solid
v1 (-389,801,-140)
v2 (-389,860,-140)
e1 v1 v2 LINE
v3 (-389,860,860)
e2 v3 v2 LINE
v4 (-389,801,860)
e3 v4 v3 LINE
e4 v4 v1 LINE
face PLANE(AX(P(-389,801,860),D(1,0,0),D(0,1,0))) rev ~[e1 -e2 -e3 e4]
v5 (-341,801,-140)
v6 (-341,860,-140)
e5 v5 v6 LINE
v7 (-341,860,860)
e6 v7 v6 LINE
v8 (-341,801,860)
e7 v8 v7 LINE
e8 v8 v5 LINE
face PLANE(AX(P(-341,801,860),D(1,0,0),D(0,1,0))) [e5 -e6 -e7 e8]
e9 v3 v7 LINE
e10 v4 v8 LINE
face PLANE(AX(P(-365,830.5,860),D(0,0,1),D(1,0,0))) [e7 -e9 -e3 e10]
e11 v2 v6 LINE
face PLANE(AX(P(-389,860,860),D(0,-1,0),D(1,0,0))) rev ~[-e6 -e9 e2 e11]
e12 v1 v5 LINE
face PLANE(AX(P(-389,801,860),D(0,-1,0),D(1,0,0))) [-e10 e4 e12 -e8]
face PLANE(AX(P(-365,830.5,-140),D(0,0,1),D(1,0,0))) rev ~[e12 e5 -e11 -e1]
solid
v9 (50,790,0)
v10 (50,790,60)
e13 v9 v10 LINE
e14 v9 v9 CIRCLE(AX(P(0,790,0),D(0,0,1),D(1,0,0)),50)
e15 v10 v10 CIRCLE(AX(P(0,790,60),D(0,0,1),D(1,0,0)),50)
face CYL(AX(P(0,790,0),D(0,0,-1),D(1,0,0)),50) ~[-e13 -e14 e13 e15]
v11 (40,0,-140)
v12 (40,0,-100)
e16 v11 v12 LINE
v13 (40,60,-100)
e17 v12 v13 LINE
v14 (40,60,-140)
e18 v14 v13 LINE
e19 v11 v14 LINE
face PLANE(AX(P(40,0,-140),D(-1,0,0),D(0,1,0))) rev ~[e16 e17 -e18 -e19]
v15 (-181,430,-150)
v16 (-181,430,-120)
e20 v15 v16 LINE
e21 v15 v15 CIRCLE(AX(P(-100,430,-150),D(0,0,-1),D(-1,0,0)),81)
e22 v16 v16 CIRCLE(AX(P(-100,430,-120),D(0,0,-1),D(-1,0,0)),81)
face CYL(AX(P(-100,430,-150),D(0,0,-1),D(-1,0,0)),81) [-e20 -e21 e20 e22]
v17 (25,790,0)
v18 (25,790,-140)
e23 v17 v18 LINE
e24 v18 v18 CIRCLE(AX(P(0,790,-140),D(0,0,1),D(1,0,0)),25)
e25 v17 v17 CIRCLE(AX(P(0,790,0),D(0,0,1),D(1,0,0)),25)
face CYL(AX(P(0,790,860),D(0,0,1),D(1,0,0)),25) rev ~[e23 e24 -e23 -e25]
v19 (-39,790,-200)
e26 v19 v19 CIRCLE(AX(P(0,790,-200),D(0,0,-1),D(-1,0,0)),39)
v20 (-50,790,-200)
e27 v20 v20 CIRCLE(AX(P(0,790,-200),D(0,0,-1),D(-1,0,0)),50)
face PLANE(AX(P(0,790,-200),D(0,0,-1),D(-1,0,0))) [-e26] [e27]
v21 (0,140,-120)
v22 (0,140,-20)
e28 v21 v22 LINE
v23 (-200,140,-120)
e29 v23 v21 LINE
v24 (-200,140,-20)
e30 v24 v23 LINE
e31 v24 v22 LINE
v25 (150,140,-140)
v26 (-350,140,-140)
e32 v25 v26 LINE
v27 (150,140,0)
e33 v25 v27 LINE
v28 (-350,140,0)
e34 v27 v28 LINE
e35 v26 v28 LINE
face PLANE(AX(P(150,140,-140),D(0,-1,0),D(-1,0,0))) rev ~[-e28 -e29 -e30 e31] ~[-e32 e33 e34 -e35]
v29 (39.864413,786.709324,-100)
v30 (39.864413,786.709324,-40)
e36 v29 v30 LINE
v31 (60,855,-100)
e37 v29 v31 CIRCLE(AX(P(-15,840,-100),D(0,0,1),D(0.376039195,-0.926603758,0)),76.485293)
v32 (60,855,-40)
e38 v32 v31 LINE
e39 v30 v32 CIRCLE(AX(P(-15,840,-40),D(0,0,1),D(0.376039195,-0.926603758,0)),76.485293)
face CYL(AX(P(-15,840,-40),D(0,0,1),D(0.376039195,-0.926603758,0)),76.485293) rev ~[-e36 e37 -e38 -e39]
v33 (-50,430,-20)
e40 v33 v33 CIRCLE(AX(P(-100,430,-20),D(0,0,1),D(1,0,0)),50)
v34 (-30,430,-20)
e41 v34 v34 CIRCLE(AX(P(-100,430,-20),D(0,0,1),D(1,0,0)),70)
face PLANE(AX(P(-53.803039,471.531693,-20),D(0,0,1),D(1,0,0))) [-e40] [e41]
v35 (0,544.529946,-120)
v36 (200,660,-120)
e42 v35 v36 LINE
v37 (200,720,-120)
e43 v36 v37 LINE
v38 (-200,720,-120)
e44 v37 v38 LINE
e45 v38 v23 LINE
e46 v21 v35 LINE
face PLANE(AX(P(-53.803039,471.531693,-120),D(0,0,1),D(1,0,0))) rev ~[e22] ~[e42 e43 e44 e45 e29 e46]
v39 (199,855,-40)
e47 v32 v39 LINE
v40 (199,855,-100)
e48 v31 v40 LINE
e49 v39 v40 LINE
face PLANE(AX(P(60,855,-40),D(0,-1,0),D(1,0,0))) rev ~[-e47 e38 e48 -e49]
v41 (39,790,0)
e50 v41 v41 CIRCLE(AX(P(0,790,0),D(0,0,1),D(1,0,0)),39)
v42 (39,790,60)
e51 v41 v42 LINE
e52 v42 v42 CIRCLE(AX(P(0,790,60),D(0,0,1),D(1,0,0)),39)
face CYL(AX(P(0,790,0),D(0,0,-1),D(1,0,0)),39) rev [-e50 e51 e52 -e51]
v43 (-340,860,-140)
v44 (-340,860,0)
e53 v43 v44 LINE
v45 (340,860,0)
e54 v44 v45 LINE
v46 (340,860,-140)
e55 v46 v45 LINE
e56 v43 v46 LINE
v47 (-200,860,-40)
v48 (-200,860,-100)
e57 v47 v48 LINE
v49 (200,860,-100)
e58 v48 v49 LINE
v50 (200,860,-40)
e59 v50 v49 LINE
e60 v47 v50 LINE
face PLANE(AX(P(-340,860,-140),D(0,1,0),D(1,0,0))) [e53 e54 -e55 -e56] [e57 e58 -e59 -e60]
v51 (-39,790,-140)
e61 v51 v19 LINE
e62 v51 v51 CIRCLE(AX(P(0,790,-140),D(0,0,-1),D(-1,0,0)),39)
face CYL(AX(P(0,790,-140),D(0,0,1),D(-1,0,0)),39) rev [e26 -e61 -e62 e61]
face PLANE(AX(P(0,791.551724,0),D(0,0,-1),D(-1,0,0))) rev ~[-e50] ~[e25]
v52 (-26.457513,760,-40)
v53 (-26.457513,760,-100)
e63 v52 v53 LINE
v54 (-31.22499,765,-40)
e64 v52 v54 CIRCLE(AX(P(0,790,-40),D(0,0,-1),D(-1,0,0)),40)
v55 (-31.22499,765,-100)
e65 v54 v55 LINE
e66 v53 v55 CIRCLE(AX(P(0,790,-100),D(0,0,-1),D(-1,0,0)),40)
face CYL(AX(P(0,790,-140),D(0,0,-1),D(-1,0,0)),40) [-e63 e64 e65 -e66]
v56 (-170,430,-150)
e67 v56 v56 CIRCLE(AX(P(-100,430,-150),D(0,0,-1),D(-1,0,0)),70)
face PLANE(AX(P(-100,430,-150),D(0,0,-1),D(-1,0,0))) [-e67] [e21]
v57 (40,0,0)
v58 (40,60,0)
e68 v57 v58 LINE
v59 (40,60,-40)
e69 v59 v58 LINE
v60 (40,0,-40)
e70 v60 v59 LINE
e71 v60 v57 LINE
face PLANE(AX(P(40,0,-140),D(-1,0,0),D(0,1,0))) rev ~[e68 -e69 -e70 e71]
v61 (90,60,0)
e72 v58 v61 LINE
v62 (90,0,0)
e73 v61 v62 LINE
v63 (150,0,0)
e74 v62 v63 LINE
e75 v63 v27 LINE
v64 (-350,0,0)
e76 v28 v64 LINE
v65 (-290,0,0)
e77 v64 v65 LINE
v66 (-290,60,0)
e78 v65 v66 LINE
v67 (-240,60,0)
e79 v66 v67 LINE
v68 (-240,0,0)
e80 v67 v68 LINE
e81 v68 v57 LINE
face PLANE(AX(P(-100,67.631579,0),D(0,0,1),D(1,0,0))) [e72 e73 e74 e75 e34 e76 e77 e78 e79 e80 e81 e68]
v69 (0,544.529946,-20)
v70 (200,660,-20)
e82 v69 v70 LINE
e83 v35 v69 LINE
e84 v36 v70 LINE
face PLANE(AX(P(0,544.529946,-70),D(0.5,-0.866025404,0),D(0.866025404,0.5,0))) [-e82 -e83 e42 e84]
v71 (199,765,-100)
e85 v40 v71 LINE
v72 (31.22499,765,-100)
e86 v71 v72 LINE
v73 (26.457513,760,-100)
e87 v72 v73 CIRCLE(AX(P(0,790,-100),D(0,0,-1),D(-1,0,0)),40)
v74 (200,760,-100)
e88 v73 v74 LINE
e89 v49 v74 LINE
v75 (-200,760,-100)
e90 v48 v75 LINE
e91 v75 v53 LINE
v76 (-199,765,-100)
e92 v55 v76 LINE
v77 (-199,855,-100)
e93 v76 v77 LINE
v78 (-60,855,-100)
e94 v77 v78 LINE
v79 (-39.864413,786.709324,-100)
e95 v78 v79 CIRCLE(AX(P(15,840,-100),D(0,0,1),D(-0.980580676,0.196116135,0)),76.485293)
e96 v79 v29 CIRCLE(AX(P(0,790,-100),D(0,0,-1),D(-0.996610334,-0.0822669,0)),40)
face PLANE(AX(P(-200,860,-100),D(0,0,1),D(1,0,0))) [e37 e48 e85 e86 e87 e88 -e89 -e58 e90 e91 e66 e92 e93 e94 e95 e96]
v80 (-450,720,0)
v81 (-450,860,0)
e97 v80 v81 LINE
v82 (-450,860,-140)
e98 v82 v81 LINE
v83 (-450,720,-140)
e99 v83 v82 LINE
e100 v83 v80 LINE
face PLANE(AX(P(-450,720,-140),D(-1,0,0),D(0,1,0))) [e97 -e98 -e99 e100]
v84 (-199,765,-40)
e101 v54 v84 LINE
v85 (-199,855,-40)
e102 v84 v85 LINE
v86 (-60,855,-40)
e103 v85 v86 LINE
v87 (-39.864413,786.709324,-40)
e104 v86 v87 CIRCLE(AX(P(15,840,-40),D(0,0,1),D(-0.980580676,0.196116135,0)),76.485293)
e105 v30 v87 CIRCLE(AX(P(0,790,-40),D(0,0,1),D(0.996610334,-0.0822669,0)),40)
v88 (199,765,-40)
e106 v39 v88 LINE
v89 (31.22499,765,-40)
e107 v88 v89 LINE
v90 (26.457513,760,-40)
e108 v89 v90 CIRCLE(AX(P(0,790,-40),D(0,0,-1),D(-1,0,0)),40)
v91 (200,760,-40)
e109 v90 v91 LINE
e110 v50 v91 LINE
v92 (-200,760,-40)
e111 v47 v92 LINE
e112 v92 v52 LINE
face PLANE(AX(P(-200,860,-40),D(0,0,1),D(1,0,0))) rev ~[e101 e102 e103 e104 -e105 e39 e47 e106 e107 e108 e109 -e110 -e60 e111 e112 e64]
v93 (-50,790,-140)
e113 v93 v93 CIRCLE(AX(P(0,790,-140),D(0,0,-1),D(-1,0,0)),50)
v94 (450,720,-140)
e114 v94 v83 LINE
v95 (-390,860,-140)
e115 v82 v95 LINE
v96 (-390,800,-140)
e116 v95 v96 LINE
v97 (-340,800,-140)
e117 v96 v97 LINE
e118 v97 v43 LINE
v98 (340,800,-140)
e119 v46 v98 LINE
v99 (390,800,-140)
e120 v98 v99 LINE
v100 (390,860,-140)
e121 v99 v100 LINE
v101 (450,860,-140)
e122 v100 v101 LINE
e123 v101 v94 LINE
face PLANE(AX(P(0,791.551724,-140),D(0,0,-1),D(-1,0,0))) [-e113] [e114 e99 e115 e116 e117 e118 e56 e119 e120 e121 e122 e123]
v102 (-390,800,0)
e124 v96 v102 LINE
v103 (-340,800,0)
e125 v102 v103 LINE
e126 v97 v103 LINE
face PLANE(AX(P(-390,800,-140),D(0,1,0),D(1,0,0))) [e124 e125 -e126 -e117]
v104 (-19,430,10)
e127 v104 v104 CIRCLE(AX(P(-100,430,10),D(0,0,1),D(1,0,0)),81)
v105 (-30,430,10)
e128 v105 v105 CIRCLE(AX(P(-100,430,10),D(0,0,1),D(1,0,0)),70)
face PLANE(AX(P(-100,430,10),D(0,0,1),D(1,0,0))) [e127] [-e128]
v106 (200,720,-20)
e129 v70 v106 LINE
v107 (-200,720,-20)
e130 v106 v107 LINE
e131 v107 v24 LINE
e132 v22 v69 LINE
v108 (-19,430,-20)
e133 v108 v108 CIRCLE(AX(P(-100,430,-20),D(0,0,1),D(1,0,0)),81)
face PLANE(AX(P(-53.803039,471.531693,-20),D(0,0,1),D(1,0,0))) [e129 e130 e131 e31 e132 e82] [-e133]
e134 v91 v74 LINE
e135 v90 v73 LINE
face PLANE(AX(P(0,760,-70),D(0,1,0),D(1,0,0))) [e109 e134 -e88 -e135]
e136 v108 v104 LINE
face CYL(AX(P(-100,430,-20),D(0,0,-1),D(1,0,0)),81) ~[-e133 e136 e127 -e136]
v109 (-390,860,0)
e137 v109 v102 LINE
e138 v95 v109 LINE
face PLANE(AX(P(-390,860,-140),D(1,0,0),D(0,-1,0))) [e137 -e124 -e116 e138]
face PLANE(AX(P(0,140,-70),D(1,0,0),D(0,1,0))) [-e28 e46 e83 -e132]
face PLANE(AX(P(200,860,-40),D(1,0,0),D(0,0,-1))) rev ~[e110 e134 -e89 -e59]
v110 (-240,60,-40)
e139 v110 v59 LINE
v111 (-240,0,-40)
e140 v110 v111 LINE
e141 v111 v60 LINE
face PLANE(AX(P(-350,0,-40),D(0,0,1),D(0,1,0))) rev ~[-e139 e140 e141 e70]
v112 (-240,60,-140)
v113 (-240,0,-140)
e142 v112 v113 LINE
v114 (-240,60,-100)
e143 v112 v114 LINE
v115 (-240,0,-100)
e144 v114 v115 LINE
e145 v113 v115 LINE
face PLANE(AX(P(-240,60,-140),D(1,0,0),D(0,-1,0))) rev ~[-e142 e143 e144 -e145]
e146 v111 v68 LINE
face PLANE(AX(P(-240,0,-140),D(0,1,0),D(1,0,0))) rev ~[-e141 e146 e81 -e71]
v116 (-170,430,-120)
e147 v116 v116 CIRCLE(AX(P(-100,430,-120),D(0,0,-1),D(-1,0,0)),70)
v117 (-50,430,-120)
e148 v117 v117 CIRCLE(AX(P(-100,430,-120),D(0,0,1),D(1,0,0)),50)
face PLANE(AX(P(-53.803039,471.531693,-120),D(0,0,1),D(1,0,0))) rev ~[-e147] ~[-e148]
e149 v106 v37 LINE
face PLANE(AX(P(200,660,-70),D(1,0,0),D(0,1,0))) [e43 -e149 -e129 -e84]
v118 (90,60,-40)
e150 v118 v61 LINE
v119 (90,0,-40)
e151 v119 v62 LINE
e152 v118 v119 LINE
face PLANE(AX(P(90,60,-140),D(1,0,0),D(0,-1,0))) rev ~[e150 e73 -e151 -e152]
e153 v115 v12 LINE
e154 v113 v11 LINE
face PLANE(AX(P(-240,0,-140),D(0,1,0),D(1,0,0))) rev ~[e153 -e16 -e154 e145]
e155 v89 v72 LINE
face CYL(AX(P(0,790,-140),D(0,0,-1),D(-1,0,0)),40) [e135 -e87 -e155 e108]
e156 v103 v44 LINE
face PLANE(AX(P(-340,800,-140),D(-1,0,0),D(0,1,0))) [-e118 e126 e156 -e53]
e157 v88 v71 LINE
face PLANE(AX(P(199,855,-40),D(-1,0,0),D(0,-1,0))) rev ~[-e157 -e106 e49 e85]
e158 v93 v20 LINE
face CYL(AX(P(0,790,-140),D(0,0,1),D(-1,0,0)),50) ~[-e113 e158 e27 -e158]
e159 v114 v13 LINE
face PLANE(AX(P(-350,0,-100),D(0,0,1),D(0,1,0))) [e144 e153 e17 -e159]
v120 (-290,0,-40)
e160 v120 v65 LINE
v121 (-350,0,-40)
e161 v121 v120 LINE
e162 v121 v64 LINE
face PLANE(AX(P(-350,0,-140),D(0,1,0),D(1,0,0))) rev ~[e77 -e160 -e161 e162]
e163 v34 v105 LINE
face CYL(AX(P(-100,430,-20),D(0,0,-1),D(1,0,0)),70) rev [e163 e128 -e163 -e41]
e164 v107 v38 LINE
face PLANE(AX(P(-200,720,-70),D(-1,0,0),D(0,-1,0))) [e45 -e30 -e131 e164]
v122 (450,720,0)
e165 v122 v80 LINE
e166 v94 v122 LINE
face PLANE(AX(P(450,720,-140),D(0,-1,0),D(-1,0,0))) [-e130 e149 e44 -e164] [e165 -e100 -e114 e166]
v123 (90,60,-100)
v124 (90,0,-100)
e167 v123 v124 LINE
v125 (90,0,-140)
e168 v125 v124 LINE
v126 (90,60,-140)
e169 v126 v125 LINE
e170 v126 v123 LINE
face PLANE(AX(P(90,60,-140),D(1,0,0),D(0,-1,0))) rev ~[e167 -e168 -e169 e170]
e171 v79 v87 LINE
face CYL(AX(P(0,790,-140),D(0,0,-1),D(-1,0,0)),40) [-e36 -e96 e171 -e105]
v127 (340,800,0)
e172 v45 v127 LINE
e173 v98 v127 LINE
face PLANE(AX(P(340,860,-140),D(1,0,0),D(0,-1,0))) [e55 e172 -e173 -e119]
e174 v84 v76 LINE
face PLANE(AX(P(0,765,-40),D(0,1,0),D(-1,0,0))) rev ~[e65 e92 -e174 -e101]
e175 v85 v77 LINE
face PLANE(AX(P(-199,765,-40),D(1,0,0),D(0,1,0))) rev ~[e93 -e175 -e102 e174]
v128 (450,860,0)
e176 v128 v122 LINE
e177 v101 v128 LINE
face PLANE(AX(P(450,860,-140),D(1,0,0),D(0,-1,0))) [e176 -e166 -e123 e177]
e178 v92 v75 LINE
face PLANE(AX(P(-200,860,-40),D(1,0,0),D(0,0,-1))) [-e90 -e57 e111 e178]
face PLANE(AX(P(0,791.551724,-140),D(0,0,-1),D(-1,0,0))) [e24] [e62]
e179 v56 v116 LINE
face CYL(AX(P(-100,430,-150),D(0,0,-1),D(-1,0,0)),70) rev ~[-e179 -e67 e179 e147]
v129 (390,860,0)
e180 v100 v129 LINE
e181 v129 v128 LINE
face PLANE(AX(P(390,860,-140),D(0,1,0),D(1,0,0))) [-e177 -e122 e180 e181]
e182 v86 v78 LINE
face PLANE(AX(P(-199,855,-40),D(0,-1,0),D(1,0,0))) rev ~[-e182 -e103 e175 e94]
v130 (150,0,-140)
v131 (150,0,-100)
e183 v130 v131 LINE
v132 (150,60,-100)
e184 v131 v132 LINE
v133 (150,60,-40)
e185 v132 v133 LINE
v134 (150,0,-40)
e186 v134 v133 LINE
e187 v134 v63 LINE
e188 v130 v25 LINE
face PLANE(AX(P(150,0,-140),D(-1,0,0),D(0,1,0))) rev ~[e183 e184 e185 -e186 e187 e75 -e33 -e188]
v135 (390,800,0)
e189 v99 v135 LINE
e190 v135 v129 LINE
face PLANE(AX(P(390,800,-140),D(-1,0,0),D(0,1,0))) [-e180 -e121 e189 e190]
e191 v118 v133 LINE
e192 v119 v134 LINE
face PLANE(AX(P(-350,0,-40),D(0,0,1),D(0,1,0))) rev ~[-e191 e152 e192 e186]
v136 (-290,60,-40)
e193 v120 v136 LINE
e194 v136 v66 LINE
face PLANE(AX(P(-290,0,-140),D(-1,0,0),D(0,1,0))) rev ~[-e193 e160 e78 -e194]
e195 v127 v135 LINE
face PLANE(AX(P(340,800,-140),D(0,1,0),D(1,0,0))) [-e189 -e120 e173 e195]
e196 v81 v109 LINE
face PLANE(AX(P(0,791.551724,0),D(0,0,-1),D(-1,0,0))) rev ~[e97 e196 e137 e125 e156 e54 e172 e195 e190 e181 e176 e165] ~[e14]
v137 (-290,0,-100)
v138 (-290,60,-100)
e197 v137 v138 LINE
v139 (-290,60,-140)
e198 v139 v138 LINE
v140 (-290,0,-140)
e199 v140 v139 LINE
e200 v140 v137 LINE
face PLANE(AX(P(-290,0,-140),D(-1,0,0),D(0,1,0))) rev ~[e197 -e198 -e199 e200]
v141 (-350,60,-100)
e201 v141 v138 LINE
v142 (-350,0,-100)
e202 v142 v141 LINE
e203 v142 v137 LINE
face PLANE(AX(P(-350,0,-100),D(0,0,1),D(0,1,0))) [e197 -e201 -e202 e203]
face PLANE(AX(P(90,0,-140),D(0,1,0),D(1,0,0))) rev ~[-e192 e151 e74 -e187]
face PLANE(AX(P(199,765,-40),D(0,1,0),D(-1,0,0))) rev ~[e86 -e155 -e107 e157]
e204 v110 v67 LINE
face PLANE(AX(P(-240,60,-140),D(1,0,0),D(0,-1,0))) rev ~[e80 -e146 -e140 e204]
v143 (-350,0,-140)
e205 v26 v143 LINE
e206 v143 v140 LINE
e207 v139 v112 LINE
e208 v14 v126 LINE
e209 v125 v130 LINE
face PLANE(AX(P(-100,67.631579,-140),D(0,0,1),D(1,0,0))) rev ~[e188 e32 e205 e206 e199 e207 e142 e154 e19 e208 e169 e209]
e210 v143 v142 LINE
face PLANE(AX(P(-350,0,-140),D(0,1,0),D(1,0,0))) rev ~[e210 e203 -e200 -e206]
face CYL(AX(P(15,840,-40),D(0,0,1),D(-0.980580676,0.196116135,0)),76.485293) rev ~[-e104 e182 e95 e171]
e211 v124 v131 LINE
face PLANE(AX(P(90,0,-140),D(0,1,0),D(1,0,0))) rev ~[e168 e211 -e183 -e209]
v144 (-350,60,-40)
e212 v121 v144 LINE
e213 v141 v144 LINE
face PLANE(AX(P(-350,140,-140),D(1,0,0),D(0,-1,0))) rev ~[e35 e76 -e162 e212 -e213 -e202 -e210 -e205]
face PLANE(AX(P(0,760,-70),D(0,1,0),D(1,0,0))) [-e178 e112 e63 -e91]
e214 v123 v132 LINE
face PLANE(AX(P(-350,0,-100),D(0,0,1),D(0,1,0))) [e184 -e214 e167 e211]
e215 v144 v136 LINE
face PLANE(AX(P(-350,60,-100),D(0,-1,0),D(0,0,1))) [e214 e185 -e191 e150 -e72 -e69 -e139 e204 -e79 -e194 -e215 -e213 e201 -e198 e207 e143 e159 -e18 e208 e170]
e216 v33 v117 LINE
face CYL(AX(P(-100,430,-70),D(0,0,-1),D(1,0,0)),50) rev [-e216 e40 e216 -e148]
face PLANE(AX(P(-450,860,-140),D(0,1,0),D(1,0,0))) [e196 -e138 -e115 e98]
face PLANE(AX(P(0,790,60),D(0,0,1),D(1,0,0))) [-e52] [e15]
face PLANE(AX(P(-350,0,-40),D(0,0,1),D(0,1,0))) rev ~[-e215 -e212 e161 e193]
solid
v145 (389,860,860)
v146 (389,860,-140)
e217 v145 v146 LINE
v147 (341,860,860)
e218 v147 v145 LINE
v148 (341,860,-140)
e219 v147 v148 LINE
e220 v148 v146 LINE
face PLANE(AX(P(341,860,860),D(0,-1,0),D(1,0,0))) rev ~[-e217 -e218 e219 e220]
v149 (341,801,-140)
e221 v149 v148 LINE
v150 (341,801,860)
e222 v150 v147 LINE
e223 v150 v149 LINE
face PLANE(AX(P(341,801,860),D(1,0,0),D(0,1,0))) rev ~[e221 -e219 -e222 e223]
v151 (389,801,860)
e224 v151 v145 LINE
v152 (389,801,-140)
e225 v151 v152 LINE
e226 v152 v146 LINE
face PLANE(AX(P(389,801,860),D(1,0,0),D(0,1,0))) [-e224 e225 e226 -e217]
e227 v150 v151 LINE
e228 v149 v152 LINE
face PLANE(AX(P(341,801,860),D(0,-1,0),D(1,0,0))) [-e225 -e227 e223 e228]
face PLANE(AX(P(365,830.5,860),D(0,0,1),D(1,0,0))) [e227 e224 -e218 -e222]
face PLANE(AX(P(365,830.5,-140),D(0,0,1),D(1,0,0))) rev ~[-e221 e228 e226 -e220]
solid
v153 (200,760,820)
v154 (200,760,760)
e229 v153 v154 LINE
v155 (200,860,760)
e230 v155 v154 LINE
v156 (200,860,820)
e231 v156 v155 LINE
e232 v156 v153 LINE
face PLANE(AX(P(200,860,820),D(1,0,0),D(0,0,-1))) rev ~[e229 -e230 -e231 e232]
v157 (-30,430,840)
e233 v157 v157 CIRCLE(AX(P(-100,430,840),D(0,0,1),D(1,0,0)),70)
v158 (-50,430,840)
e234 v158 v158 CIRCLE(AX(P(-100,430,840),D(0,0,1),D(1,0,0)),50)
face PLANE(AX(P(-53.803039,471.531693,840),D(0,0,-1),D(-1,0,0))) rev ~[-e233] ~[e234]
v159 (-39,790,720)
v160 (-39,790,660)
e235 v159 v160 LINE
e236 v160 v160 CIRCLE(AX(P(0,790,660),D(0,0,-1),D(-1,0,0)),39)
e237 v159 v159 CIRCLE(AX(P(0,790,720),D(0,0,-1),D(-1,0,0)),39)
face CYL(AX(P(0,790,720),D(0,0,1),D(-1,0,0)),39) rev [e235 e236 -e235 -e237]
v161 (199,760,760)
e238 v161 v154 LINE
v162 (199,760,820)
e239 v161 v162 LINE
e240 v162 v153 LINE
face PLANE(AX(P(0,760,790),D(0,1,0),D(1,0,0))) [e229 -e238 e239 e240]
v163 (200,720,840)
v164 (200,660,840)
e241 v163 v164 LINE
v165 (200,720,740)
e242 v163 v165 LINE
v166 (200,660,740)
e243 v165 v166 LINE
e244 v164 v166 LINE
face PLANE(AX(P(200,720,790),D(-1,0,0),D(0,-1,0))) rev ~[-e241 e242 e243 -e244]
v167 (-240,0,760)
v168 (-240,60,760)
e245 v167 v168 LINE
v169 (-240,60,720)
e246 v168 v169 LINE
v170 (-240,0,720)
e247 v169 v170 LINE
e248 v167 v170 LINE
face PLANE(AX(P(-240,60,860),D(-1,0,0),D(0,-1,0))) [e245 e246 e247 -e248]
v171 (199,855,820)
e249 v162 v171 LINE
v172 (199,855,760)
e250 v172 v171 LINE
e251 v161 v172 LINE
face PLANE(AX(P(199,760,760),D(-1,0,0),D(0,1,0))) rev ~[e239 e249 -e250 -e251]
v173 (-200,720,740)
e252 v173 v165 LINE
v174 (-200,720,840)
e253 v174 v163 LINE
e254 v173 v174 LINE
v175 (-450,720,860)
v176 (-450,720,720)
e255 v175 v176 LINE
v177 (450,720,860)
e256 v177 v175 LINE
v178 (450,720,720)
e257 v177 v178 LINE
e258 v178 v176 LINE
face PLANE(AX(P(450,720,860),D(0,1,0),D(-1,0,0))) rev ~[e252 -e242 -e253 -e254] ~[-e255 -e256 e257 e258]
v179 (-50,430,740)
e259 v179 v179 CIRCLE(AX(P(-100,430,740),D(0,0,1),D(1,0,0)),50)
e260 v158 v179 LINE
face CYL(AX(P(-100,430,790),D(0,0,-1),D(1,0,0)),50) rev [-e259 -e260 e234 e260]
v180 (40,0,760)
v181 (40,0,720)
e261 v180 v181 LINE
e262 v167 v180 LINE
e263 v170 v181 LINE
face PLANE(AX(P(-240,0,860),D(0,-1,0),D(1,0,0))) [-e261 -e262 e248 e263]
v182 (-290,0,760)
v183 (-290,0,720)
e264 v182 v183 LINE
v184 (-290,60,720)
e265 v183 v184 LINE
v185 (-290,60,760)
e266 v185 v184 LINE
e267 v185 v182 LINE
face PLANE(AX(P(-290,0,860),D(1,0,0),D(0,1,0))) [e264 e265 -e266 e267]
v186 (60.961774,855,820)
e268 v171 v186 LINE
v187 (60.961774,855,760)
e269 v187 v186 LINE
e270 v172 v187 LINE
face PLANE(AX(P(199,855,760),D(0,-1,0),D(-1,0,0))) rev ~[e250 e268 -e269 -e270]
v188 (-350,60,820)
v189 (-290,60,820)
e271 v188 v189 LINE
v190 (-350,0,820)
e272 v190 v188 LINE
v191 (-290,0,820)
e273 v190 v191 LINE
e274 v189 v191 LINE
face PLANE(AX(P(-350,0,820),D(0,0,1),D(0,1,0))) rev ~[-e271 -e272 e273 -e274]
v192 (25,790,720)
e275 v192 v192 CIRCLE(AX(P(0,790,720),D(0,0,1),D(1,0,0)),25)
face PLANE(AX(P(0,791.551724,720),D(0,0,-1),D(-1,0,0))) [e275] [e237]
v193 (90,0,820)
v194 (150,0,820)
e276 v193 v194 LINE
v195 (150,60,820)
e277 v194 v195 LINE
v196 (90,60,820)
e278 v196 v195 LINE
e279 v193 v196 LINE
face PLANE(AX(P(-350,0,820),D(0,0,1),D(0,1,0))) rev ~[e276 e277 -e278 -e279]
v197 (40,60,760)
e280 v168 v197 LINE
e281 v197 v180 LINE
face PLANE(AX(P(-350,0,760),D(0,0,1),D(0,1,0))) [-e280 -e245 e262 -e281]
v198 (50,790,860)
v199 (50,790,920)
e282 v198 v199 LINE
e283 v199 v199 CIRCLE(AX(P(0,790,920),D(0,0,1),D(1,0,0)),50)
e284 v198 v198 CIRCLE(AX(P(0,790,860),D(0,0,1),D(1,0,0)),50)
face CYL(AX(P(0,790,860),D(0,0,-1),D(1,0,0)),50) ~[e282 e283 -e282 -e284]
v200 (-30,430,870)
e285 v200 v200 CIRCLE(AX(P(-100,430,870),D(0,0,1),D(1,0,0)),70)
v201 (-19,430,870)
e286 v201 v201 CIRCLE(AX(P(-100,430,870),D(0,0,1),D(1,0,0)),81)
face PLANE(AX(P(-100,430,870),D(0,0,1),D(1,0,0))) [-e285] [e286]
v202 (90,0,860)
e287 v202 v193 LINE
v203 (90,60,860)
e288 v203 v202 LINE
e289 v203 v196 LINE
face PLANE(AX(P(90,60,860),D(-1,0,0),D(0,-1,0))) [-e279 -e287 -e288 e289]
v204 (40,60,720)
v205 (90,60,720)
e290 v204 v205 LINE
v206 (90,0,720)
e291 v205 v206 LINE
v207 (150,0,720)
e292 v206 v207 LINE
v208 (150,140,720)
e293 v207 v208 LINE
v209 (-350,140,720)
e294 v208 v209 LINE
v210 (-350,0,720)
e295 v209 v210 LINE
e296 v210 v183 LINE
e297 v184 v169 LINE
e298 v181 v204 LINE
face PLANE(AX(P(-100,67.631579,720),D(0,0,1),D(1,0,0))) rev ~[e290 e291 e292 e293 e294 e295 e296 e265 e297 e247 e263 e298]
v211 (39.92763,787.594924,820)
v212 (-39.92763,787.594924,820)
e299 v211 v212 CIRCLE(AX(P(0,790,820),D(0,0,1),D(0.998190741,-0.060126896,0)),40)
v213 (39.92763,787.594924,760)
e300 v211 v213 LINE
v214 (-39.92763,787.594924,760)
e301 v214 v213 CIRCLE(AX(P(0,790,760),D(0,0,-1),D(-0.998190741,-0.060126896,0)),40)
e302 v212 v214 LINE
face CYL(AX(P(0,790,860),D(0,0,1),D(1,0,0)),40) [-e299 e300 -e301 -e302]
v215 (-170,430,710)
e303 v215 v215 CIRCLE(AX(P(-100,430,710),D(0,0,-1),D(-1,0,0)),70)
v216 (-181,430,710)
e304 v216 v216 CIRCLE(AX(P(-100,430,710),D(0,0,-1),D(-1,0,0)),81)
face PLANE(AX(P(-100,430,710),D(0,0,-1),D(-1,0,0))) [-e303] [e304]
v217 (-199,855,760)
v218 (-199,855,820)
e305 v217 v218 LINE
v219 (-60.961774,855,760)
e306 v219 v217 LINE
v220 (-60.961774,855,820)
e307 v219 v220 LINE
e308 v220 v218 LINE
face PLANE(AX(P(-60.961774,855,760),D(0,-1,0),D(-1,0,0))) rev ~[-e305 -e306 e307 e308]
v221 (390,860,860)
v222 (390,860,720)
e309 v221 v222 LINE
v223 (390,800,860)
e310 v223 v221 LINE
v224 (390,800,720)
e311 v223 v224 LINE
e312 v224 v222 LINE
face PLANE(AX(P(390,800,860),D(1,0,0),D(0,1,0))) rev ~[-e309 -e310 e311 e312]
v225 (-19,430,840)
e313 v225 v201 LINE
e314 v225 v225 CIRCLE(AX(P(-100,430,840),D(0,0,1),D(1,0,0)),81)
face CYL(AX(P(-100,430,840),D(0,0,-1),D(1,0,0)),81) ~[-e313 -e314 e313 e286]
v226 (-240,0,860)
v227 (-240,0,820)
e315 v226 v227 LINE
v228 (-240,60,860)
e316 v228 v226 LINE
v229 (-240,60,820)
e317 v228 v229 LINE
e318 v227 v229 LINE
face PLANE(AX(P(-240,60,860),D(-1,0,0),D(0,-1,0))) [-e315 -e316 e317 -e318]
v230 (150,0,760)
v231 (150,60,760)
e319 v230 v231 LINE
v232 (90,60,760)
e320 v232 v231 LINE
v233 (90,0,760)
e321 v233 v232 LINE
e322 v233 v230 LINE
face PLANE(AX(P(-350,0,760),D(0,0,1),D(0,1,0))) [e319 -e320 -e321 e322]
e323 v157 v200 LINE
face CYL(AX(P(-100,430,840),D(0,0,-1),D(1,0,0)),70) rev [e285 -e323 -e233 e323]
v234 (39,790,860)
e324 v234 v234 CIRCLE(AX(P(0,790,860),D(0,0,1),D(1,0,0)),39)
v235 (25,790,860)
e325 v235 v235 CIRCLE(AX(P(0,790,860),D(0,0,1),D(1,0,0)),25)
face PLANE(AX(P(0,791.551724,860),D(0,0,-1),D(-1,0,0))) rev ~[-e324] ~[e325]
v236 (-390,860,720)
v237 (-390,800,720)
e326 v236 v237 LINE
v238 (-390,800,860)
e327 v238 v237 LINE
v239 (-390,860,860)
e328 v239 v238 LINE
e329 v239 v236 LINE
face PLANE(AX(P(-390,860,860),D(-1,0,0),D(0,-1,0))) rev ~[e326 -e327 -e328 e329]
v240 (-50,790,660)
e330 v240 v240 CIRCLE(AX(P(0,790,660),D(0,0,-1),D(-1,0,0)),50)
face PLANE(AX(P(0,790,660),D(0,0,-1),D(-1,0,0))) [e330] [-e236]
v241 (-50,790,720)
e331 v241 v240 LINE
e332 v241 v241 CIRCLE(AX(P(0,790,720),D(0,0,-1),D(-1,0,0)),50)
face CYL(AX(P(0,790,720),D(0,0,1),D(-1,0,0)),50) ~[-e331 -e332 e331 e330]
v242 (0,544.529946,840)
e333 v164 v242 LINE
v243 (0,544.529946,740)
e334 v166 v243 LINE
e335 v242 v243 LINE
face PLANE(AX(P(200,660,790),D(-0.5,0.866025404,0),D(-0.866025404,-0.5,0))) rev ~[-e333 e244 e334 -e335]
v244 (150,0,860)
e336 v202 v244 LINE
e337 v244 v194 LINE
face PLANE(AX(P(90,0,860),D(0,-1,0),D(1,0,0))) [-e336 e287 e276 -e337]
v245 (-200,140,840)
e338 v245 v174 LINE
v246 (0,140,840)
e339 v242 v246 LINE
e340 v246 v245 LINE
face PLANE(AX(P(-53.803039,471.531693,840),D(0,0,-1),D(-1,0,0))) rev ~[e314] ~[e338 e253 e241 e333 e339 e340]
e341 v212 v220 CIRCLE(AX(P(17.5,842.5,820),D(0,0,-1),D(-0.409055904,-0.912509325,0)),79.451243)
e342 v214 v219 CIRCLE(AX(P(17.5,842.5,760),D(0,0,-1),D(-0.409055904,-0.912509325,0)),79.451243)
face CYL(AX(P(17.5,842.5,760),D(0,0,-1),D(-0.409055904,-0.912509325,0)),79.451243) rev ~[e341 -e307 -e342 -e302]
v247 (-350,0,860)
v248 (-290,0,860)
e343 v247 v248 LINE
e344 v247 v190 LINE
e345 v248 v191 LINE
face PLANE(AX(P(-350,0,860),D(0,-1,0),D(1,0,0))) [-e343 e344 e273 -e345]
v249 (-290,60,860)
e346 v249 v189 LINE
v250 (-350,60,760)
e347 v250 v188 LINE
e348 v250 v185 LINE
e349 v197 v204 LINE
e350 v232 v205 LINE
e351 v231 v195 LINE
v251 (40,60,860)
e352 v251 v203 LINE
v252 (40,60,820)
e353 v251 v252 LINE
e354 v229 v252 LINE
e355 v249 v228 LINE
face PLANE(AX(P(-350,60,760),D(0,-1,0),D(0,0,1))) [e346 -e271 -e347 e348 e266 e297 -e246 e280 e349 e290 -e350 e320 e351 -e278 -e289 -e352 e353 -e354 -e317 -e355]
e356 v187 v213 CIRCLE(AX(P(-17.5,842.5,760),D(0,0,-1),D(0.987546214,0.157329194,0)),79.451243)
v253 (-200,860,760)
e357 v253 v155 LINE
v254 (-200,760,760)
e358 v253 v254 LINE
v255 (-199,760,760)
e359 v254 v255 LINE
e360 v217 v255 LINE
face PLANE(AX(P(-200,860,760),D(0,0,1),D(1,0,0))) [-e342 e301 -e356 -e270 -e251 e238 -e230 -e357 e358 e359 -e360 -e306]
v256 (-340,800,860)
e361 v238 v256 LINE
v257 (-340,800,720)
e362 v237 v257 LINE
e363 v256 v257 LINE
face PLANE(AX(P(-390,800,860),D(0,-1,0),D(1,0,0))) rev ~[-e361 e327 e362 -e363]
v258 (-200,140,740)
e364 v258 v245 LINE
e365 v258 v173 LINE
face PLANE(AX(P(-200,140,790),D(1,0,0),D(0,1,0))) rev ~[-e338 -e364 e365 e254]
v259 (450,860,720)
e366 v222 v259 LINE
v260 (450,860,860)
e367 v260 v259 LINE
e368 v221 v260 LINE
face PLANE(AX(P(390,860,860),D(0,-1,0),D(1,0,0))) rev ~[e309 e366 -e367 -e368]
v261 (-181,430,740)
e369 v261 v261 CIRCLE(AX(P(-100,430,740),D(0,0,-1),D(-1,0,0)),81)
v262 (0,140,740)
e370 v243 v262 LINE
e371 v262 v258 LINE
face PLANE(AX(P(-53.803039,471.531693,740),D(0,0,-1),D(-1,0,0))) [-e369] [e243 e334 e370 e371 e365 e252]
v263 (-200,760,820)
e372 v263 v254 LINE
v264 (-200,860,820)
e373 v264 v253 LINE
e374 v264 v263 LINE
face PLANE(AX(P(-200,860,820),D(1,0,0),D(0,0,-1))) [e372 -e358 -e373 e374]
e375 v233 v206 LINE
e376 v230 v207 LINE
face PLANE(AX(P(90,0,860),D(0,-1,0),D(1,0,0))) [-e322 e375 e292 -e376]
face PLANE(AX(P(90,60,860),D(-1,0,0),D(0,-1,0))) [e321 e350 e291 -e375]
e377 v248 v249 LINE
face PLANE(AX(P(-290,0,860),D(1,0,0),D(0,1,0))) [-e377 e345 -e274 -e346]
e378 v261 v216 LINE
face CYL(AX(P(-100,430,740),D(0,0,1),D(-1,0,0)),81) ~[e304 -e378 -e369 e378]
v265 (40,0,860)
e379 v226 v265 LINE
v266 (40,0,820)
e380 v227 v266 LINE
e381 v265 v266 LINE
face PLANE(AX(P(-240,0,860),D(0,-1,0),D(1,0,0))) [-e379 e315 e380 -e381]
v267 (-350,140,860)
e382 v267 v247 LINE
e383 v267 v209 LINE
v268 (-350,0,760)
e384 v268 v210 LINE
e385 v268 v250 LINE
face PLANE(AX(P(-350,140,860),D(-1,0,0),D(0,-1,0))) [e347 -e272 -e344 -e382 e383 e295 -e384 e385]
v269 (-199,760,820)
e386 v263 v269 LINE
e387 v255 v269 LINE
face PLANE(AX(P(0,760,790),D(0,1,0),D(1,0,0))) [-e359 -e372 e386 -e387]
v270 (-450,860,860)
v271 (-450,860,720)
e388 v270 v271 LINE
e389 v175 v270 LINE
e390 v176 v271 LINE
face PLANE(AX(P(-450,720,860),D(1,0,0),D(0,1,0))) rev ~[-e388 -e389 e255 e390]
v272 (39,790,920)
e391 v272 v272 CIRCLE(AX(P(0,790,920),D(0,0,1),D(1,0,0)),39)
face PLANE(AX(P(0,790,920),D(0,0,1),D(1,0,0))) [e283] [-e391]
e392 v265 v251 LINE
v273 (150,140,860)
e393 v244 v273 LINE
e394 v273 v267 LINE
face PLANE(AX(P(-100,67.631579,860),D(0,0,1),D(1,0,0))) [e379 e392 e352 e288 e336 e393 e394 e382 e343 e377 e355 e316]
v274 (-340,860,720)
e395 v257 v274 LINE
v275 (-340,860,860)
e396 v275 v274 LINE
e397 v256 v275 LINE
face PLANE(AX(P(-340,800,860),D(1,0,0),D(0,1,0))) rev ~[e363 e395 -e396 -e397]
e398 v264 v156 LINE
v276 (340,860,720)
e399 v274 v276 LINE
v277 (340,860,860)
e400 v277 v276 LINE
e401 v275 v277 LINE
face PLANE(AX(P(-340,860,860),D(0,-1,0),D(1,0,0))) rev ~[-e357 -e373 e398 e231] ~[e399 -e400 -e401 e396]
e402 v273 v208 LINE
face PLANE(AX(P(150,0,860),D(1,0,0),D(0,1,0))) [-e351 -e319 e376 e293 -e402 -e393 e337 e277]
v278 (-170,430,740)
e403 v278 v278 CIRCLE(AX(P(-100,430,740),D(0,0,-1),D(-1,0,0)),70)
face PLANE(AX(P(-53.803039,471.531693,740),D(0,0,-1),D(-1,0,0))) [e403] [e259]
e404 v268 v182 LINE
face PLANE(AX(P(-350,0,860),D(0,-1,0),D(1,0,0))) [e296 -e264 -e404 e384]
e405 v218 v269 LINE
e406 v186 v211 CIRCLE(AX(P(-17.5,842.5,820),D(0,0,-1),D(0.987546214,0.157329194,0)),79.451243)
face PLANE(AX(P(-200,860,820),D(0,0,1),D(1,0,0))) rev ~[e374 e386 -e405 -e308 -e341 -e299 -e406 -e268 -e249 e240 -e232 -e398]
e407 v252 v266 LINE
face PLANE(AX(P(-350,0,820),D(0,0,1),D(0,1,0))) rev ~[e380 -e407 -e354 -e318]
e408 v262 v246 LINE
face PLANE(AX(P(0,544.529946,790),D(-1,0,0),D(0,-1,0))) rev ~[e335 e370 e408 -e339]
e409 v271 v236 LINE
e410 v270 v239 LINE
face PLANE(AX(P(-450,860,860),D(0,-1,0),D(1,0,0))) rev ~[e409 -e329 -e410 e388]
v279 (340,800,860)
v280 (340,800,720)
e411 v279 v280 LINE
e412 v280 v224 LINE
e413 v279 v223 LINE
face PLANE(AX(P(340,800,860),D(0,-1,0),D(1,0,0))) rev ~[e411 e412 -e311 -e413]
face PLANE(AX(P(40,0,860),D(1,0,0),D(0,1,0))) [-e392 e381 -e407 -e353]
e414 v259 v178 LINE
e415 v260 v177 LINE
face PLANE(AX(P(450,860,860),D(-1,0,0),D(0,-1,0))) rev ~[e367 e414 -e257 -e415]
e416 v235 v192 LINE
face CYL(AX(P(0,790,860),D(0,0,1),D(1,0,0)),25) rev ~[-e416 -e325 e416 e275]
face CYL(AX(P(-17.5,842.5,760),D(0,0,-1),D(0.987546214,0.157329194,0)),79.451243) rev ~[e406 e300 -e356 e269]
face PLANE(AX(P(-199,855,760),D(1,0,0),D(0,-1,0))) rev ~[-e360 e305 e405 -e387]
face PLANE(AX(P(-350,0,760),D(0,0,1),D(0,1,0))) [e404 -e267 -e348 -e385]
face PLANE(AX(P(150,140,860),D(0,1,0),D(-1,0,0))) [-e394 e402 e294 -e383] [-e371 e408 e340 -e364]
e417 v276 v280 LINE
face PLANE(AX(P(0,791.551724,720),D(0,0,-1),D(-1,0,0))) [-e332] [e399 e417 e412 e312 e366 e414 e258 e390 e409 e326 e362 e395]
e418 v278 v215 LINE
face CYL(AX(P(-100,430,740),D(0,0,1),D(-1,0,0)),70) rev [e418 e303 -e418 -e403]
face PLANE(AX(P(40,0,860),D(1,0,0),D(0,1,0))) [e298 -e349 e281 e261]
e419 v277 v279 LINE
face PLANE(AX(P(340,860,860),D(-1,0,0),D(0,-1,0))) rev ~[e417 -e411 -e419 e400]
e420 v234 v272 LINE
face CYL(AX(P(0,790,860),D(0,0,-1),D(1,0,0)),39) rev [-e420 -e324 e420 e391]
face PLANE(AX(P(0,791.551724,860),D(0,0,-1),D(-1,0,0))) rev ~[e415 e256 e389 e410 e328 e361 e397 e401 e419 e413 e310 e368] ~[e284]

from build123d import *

# Parameters (mm, degrees)
FOOT_BASE_DEPTH               = 140
FOOT_BLOCK_SKETCH_W           = 500
FOOT_BLOCK_SKETCH_H           = 140
FOOT_BLOCK_DEPTH              = 140
FOOT_SLOT_SKETCH_W            = 50
FOOT_SLOT_SKETCH_H            = 60
FOOT_SLOT_CUT_DEPTH           = 140
FOOT_NOTCH_SKETCH_W           = 60
FOOT_NOTCH_SKETCH_H           = 60
FOOT_NOTCH_CUT_DEPTH          = 500
UPRIGHT_COLUMN_DEPTH          = 500
COLUMN_RELIEF_SKETCH_W        = 50
COLUMN_RELIEF_SKETCH_H        = 60
COLUMN_RELIEF_CUT_DEPTH       = 500
TOP_BEAM_DEPTH                = 140
TOP_BEAM_EXTENSION_DEPTH      = 140
CROSS_RAILS_SKETCH_W          = 48
CROSS_RAILS_SKETCH_H          = 59
CROSS_RAILS_DEPTH             = 1000
CROSS_RAILS_2_DEPTH           = 1000
AXLE_BORE_50_SKETCH_R         = 25
AXLE_BORE_50_DEPTH            = 1000
BEAM_POCKET_SKETCH_W          = 400
BEAM_POCKET_SKETCH_H          = 60
BEAM_POCKET_CUT_DEPTH         = 100
POCKET_INSERT_A_DEPTH         = 60
POCKET_INSERT_B_DEPTH         = 60
POCKET_INSERT_B_2_DEPTH       = 60
ROLLER_80_A_SKETCH_R          = 40
ROLLER_80_A_DEPTH             = 140
ROLLER_80_B_SKETCH_R          = 40
ROLLER_80_B_DEPTH             = 140
BUSHING_RING_100_A_SKETCH_R   = 50
BUSHING_RING_100_A_SKETCH_R_2 = 39
BUSHING_RING_100_A_DEPTH      = 60
BUSHING_BORE_50_SKETCH_R      = 25
BUSHING_BORE_50_DEPTH         = 1000
BUSHING_RING_100_B_SKETCH_R   = 50
BUSHING_RING_100_B_SKETCH_R_2 = 39
BUSHING_RING_100_B_DEPTH      = 60
BUSHING_RING_100_C_SKETCH_R   = 50
BUSHING_RING_100_C_SKETCH_R_2 = 39
BUSHING_RING_100_C_DEPTH      = 60
BUSHING_RING_100_D_SKETCH_R   = 50
BUSHING_RING_100_D_SKETCH_R_2 = 39
BUSHING_RING_100_D_DEPTH      = 60
SECOND_TRESTLE_BEAM_SKETCH_R  = 50
SECOND_TRESTLE_BEAM_DEPTH     = 50
SECOND_COLUMN_SKETCH_R        = 50
SECOND_COLUMN_DEPTH           = 50
RAIL_CLEARANCE_SKETCH_W       = 500
RAIL_CLEARANCE_SKETCH_H       = 140
RAIL_CLEARANCE_CUT_DEPTH      = 1000
SECOND_FOOT_BASE_DEPTH        = 140
SECOND_FOOT_BLOCK_DEPTH       = 140
SECOND_FOOT_NOTCH_SKETCH_W    = 60
SECOND_FOOT_NOTCH_SKETCH_H    = 60
SECOND_FOOT_NOTCH_CUT_DEPTH   = 500
COLUMN_RING_140_A_SKETCH_R    = 81
COLUMN_RING_140_A_SKETCH_R_2  = 70
COLUMN_RING_140_A_DEPTH       = 30
COLUMN_RING_140_B_SKETCH_R    = 81
COLUMN_RING_140_B_SKETCH_R_2  = 70
COLUMN_RING_140_B_DEPTH       = 30
COLUMN_RING_140_C_SKETCH_R    = 81
COLUMN_RING_140_C_SKETCH_R_2  = 70
COLUMN_RING_140_C_DEPTH       = 30
COLUMN_START                  = 30
COLUMN_RING_140_D_SKETCH_R    = 81
COLUMN_RING_140_D_SKETCH_R_2  = 70
COLUMN_RING_140_D_DEPTH       = 30


with BuildPart() as part:
    # Foot Base Sketch → Foot Base (new body)
    with BuildSketch(Plane(origin=(0, 0, 0), x_dir=(1, 0, 0), z_dir=(0, 1, 0))):
        Polygon((-250, 0), (-250, 140), (-190, 140), (-190, 80), (-140, 80), (-140, 140), (140, 140), (140, 80), (190, 80), (190, 140), (250, 140), (250, 0), align=None)
    extrude(amount=FOOT_BASE_DEPTH)

    # Foot Block Sketch → Foot Block (add)
    with BuildSketch(Plane.XY):
        with Locations((0, 70)):
            Rectangle(FOOT_BLOCK_SKETCH_W, FOOT_BLOCK_SKETCH_H)
    extrude(amount=-FOOT_BLOCK_DEPTH)

    # Foot Slot Sketch → Foot Slot Cut (cut)
    with BuildSketch(Plane.XY):
        with Locations((-165, 30)):
            Rectangle(FOOT_SLOT_SKETCH_W, FOOT_SLOT_SKETCH_H)
        with Locations((165, 30)):
            Rectangle(FOOT_SLOT_SKETCH_W, FOOT_SLOT_SKETCH_H)
    extrude(amount=-FOOT_SLOT_CUT_DEPTH, mode=Mode.SUBTRACT)

    # Foot Notch Sketch → Foot Notch Cut (cut)
    with BuildSketch(Plane.ZY.offset(250)):
        with Locations((-70, 30)):
            Rectangle(FOOT_NOTCH_SKETCH_W, FOOT_NOTCH_SKETCH_H)
    extrude(amount=-FOOT_NOTCH_CUT_DEPTH, mode=Mode.SUBTRACT)



with BuildPart() as body_2:
    # Upright Column Sketch → Upright Column (new body)
    with BuildSketch(Plane.ZY.offset(250)):
        Polygon((760, 60), (820, 60), (820, 0), (860, 0), (860, 140), (720, 140), (720, 0), (760, 0), align=None)
    extrude(amount=-UPRIGHT_COLUMN_DEPTH)

    # Column Relief Sketch → Column Relief Cut (cut)
    with BuildSketch(Plane(origin=(0, 0, 720), x_dir=(-1, 0, 0), z_dir=(0, 0, -1))):
        with Locations((-165, 30)):
            Rectangle(COLUMN_RELIEF_SKETCH_W, COLUMN_RELIEF_SKETCH_H)
        with Locations((165, 30)):
            Rectangle(COLUMN_RELIEF_SKETCH_W, COLUMN_RELIEF_SKETCH_H)
    extrude(amount=-COLUMN_RELIEF_CUT_DEPTH, mode=Mode.SUBTRACT)



with BuildPart() as body_3:
    # Top Beam Sketch → Top Beam (new body)
    with BuildSketch(Plane.XY.offset(860)):
        Polygon((450, 720), (-450, 720), (-450, 860), (-390, 860), (-390, 800), (-340, 800), (-340, 860), (340, 860), (340, 800), (390, 800), (390, 860), (450, 860), align=None)
    extrude(amount=-TOP_BEAM_DEPTH)


with BuildPart() as body_4:
    # Top Beam Extension Sketch → Top Beam Extension (new body)
    with BuildSketch(Plane(origin=(0, 0, -140), x_dir=(-1, 0, 0), z_dir=(0, 0, -1))):
        Polygon((-450, 860), (-450, 720), (450, 720), (450, 860), (390, 860), (390, 800), (340, 800), (340, 860), (-340, 860), (-340, 800), (-390, 800), (-390, 860), align=None)
    extrude(amount=-TOP_BEAM_EXTENSION_DEPTH)


with BuildPart() as body_5:
    # Cross Rails Sketch → Cross Rails (new body)
    with BuildSketch(Plane.XY.offset(860)):
        with Locations((-365, 830.5)):
            Rectangle(CROSS_RAILS_SKETCH_W, CROSS_RAILS_SKETCH_H)
    extrude(amount=-CROSS_RAILS_DEPTH)


with BuildPart() as body_6:
    # Cross Rails Sketch → Cross Rails 2 (new body)
    with BuildSketch(Plane.XY.offset(860)):
        with Locations((365, 830.5)):
            Rectangle(CROSS_RAILS_SKETCH_W, CROSS_RAILS_SKETCH_H)
    extrude(amount=-CROSS_RAILS_2_DEPTH)


with BuildPart() as axle_bore_50_tool:
    # Axle Bore Ø50 Sketch → Axle Bore Ø50 (new body)
    with BuildSketch(Plane.XY.offset(860)):
        with Locations((0, 790)):
            Circle(AXLE_BORE_50_SKETCH_R)
    extrude(amount=-AXLE_BORE_50_DEPTH)


with BuildPart() as body_3_1:
    add(body_3.part)

    # Axle Bore Ø50: cut by axle_bore_50_tool
    add(axle_bore_50_tool.part, mode=Mode.SUBTRACT)


with BuildPart() as body_4_1:
    add(body_4.part)

    # Axle Bore Ø50: cut by axle_bore_50_tool
    add(axle_bore_50_tool.part, mode=Mode.SUBTRACT)


with BuildPart() as beam_pocket_cut_tool:
    # Beam Pocket Sketch → Beam Pocket Cut (new body)
    with BuildSketch(Plane(origin=(0, 860, 0), x_dir=(1, 0, 0), z_dir=(0, 1, 0))):
        with Locations((0, -790)):
            Rectangle(BEAM_POCKET_SKETCH_W, BEAM_POCKET_SKETCH_H)
        with Locations((0, 70)):
            Rectangle(BEAM_POCKET_SKETCH_W, BEAM_POCKET_SKETCH_H)
    extrude(amount=-BEAM_POCKET_CUT_DEPTH)


with BuildPart() as body_3_2:
    add(body_3_1.part)

    # Beam Pocket Cut: cut by beam_pocket_cut_tool
    add(beam_pocket_cut_tool.part, mode=Mode.SUBTRACT)

    # Pocket Insert A Sketch → Pocket Insert A (add)
    with BuildSketch(Plane.XY.offset(760)):
        with BuildLine():
            Line((-60.961774132, 855), (-199, 855))
            Line((-199, 855), (-199, 760))
            Line((-199, 760), (199, 760))
            Line((199, 760), (199, 855))
            Line((199, 855), (60.961774132, 855))
            ThreePointArc((60.961774132, 855), (52.388331141, 804.709509525), (15, 770))
            ThreePointArc((15, 770), (7.90569415, 766.282917549), (0, 765))
            ThreePointArc((0, 765), (-7.90569415, 766.282917549), (-15, 770))
            ThreePointArc((-15, 770), (-52.388331141, 804.709509525), (-60.961774132, 855))
        make_face()
    extrude(amount=POCKET_INSERT_A_DEPTH)

    # Roller Ø80 A Sketch → Roller Ø80 A (add)
    with BuildSketch(Plane.XY.offset(860)):
        with Locations((0, 790)):
            Circle(ROLLER_80_A_SKETCH_R)
    extrude(amount=-ROLLER_80_A_DEPTH)

    # Bushing Ring Ø100 A Sketch → Bushing Ring Ø100 A (add)
    with BuildSketch(Plane.XY.offset(860)):
        with Locations((0, 790)):
            Circle(BUSHING_RING_100_A_SKETCH_R)
        with Locations((0, 790)):
            Circle(BUSHING_RING_100_A_SKETCH_R_2, mode=Mode.SUBTRACT)
    extrude(amount=BUSHING_RING_100_A_DEPTH)


with BuildPart() as body_4_2:
    add(body_4_1.part)

    # Beam Pocket Cut: cut by beam_pocket_cut_tool
    add(beam_pocket_cut_tool.part, mode=Mode.SUBTRACT)



with BuildPart() as body_7:
    # Pocket Insert B Sketch → Pocket Insert B (new body)
    with BuildSketch(Plane(origin=(0, 0, -40), x_dir=(-1, 0, 0), z_dir=(0, 0, -1))):
        with BuildLine():
            Line((-60, 855), (-199, 855))
            Line((-199, 855), (-199, 765))
            Line((-199, 765), (0, 765))
            ThreePointArc((0, 765), (-7.183697139, 766.054342869), (-13.76146789, 769.128440367))
            ThreePointArc((-13.76146789, 769.128440367), (-52.343089795, 803.738336264), (-60, 855))
        make_face()
    extrude(amount=POCKET_INSERT_B_DEPTH)


with BuildPart() as body_8:
    # Pocket Insert B Sketch → Pocket Insert B 2 (new body)
    with BuildSketch(Plane(origin=(0, 0, -40), x_dir=(-1, 0, 0), z_dir=(0, 0, -1))):
        with BuildLine():
            ThreePointArc((13.76146789, 769.128440367), (7.183697139, 766.054342869), (0, 765))
            Line((0, 765), (199, 765))
            Line((199, 765), (199, 855))
            Line((199, 855), (60, 855))
            ThreePointArc((60, 855), (52.343089795, 803.738336264), (13.76146789, 769.128440367))
        make_face()
    extrude(amount=POCKET_INSERT_B_2_DEPTH)


with BuildPart() as body_4_3:
    add(body_4_2.part)

    add(body_7.part)  # Roller Ø80 B merges body 7

    add(body_8.part)  # Roller Ø80 B merges body 8
    # Roller Ø80 B Sketch → Roller Ø80 B (add)
    with BuildSketch(Plane(origin=(0, 0, -140), x_dir=(-1, 0, 0), z_dir=(0, 0, -1))):
        with Locations((0, 790)):
            Circle(ROLLER_80_B_SKETCH_R)
    extrude(amount=-ROLLER_80_B_DEPTH)


with BuildPart() as bushing_bore_50_tool:
    # Bushing Bore Ø50 Sketch → Bushing Bore Ø50 (new body)
    with BuildSketch(Plane.XY.offset(860)):
        with Locations((0, 790)):
            Circle(BUSHING_BORE_50_SKETCH_R)
    extrude(amount=-BUSHING_BORE_50_DEPTH)


with BuildPart() as body_3_3:
    add(body_3_2.part)

    # Bushing Bore Ø50: cut by bushing_bore_50_tool
    add(bushing_bore_50_tool.part, mode=Mode.SUBTRACT)

    # Bushing Ring Ø100 B Sketch → Bushing Ring Ø100 B (add)
    with BuildSketch(Plane(origin=(0, 0, 720), x_dir=(-1, 0, 0), z_dir=(0, 0, -1))):
        with Locations((0, 790)):
            Circle(BUSHING_RING_100_B_SKETCH_R)
        with Locations((0, 790)):
            Circle(BUSHING_RING_100_B_SKETCH_R_2, mode=Mode.SUBTRACT)
    extrude(amount=BUSHING_RING_100_B_DEPTH)


with BuildPart() as body_4_4:
    add(body_4_3.part)

    # Bushing Bore Ø50: cut by bushing_bore_50_tool
    add(bushing_bore_50_tool.part, mode=Mode.SUBTRACT)

    # Bushing Ring Ø100 C Sketch → Bushing Ring Ø100 C (add)
    with BuildSketch(Plane.XY):
        with Locations((0, 790)):
            Circle(BUSHING_RING_100_C_SKETCH_R)
        with Locations((0, 790)):
            Circle(BUSHING_RING_100_C_SKETCH_R_2, mode=Mode.SUBTRACT)
    extrude(amount=BUSHING_RING_100_C_DEPTH)

    # Bushing Ring Ø100 D Sketch → Bushing Ring Ø100 D (add)
    with BuildSketch(Plane(origin=(0, 0, -140), x_dir=(-1, 0, 0), z_dir=(0, 0, -1))):
        with Locations((0, 790)):
            Circle(BUSHING_RING_100_D_SKETCH_R)
        with Locations((0, 790)):
            Circle(BUSHING_RING_100_D_SKETCH_R_2, mode=Mode.SUBTRACT)
    extrude(amount=BUSHING_RING_100_D_DEPTH)


with BuildPart() as part_1:
    add(part.part)

    add(body_4_4.part)  # Second Trestle Beam merges body 4
    # Second Trestle Beam Sketch → Second Trestle Beam (add, symmetric)
    with BuildSketch(Plane.XY.offset(-70)):
        Polygon((-200, 140), (0, 140), (0, 544.529946162), (200, 660), (200, 720), (-200, 720), align=None)
        with Locations((-100, 430)):
            Circle(SECOND_TRESTLE_BEAM_SKETCH_R, mode=Mode.SUBTRACT)
    extrude(amount=SECOND_TRESTLE_BEAM_DEPTH, both=True)


with BuildPart() as body_2_1:
    add(body_2.part)

    add(body_3_3.part)  # Second Column merges body 3
    # Second Column Sketch → Second Column (add, symmetric)
    with BuildSketch(Plane.XY.offset(790)):
        Polygon((-200, 720), (200, 720), (200, 660), (0, 544.529946162), (0, 140), (-200, 140), align=None)
        with Locations((-100, 430)):
            Circle(SECOND_COLUMN_SKETCH_R, mode=Mode.SUBTRACT)
    extrude(amount=SECOND_COLUMN_DEPTH, both=True)


with BuildPart() as rail_clearance_cut_tool:
    # Rail Clearance Sketch → Rail Clearance Cut (new body)
    with BuildSketch(Plane.XY.offset(860)):
        with Locations((0, 70)):
            Rectangle(RAIL_CLEARANCE_SKETCH_W, RAIL_CLEARANCE_SKETCH_H)
    extrude(amount=-RAIL_CLEARANCE_CUT_DEPTH)


with BuildPart() as part_2:
    add(part_1.part)

    # Rail Clearance Cut: cut by rail_clearance_cut_tool
    add(rail_clearance_cut_tool.part, mode=Mode.SUBTRACT)

    # Second Foot Block Sketch → Second Foot Block (add)
    with BuildSketch(Plane(origin=(0, 0, -140), x_dir=(-1, 0, 0), z_dir=(0, 0, -1))):
        Polygon((-150, 140), (350, 140), (350, 0), (290, 0), (290, 60), (240, 60), (240, 0), (-40, 0), (-40, 60), (-90, 60), (-90, 0), (-150, 0), align=None)
    extrude(amount=-SECOND_FOOT_BLOCK_DEPTH)


with BuildPart() as body_2_2:
    add(body_2_1.part)

    # Rail Clearance Cut: cut by rail_clearance_cut_tool
    add(rail_clearance_cut_tool.part, mode=Mode.SUBTRACT)

    # Second Foot Base Sketch → Second Foot Base (add)
    with BuildSketch(Plane.XY.offset(860)):
        Polygon((-350, 140), (-350, 0), (-290, 0), (-290, 60), (-240, 60), (-240, 0), (40, 0), (40, 60), (90, 60), (90, 0), (150, 0), (150, 140), align=None)
    extrude(amount=-SECOND_FOOT_BASE_DEPTH)


with BuildPart() as second_foot_notch_cut_tool:
    # Second Foot Notch Sketch → Second Foot Notch Cut (new body)
    with BuildSketch(Plane.ZY.offset(350)):
        with Locations((-70, 30)):
            Rectangle(SECOND_FOOT_NOTCH_SKETCH_W, SECOND_FOOT_NOTCH_SKETCH_H)
        with Locations((790, 30)):
            Rectangle(SECOND_FOOT_NOTCH_SKETCH_W, SECOND_FOOT_NOTCH_SKETCH_H)
    extrude(amount=-SECOND_FOOT_NOTCH_CUT_DEPTH)


with BuildPart() as part_3:
    add(part_2.part)

    # Second Foot Notch Cut: cut by second_foot_notch_cut_tool
    add(second_foot_notch_cut_tool.part, mode=Mode.SUBTRACT)

    # Column Ring Ø140 C Sketch → Column Ring Ø140 C (add)
    with BuildSketch(Plane.XY.offset(-20)):
        with Locations((-100, 430)):
            Circle(COLUMN_RING_140_C_SKETCH_R)
        with Locations((-100, 430)):
            Circle(COLUMN_RING_140_C_SKETCH_R_2, mode=Mode.SUBTRACT)
    extrude(amount=COLUMN_RING_140_C_DEPTH)

    # Column Ring Ø140 D Sketch → Column Ring Ø140 D (add)
    with BuildSketch(Plane(origin=(0, 0, -120), x_dir=(-1, 0, 0), z_dir=(0, 0, -1)).offset(COLUMN_START)):
        with Locations((100, 430)):
            Circle(COLUMN_RING_140_D_SKETCH_R)
        with Locations((100, 430)):
            Circle(COLUMN_RING_140_D_SKETCH_R_2, mode=Mode.SUBTRACT)
    extrude(amount=-COLUMN_RING_140_D_DEPTH)


with BuildPart() as body_2_3:
    add(body_2_2.part)

    # Second Foot Notch Cut: cut by second_foot_notch_cut_tool
    add(second_foot_notch_cut_tool.part, mode=Mode.SUBTRACT)

    # Column Ring Ø140 A Sketch → Column Ring Ø140 A (add)
    with BuildSketch(Plane.XY.offset(840)):
        with Locations((-100, 430)):
            Circle(COLUMN_RING_140_A_SKETCH_R)
        with Locations((-100, 430)):
            Circle(COLUMN_RING_140_A_SKETCH_R_2, mode=Mode.SUBTRACT)
    extrude(amount=COLUMN_RING_140_A_DEPTH)

    # Column Ring Ø140 B Sketch → Column Ring Ø140 B (add)
    with BuildSketch(Plane(origin=(0, 0, 740), x_dir=(-1, 0, 0), z_dir=(0, 0, -1))):
        with Locations((100, 430)):
            Circle(COLUMN_RING_140_B_SKETCH_R)
        with Locations((100, 430)):
            Circle(COLUMN_RING_140_B_SKETCH_R_2, mode=Mode.SUBTRACT)
    extrude(amount=COLUMN_RING_140_B_DEPTH)


solid = Compound([body_5.part, body_6.part, part_3.part, body_2_3.part])
